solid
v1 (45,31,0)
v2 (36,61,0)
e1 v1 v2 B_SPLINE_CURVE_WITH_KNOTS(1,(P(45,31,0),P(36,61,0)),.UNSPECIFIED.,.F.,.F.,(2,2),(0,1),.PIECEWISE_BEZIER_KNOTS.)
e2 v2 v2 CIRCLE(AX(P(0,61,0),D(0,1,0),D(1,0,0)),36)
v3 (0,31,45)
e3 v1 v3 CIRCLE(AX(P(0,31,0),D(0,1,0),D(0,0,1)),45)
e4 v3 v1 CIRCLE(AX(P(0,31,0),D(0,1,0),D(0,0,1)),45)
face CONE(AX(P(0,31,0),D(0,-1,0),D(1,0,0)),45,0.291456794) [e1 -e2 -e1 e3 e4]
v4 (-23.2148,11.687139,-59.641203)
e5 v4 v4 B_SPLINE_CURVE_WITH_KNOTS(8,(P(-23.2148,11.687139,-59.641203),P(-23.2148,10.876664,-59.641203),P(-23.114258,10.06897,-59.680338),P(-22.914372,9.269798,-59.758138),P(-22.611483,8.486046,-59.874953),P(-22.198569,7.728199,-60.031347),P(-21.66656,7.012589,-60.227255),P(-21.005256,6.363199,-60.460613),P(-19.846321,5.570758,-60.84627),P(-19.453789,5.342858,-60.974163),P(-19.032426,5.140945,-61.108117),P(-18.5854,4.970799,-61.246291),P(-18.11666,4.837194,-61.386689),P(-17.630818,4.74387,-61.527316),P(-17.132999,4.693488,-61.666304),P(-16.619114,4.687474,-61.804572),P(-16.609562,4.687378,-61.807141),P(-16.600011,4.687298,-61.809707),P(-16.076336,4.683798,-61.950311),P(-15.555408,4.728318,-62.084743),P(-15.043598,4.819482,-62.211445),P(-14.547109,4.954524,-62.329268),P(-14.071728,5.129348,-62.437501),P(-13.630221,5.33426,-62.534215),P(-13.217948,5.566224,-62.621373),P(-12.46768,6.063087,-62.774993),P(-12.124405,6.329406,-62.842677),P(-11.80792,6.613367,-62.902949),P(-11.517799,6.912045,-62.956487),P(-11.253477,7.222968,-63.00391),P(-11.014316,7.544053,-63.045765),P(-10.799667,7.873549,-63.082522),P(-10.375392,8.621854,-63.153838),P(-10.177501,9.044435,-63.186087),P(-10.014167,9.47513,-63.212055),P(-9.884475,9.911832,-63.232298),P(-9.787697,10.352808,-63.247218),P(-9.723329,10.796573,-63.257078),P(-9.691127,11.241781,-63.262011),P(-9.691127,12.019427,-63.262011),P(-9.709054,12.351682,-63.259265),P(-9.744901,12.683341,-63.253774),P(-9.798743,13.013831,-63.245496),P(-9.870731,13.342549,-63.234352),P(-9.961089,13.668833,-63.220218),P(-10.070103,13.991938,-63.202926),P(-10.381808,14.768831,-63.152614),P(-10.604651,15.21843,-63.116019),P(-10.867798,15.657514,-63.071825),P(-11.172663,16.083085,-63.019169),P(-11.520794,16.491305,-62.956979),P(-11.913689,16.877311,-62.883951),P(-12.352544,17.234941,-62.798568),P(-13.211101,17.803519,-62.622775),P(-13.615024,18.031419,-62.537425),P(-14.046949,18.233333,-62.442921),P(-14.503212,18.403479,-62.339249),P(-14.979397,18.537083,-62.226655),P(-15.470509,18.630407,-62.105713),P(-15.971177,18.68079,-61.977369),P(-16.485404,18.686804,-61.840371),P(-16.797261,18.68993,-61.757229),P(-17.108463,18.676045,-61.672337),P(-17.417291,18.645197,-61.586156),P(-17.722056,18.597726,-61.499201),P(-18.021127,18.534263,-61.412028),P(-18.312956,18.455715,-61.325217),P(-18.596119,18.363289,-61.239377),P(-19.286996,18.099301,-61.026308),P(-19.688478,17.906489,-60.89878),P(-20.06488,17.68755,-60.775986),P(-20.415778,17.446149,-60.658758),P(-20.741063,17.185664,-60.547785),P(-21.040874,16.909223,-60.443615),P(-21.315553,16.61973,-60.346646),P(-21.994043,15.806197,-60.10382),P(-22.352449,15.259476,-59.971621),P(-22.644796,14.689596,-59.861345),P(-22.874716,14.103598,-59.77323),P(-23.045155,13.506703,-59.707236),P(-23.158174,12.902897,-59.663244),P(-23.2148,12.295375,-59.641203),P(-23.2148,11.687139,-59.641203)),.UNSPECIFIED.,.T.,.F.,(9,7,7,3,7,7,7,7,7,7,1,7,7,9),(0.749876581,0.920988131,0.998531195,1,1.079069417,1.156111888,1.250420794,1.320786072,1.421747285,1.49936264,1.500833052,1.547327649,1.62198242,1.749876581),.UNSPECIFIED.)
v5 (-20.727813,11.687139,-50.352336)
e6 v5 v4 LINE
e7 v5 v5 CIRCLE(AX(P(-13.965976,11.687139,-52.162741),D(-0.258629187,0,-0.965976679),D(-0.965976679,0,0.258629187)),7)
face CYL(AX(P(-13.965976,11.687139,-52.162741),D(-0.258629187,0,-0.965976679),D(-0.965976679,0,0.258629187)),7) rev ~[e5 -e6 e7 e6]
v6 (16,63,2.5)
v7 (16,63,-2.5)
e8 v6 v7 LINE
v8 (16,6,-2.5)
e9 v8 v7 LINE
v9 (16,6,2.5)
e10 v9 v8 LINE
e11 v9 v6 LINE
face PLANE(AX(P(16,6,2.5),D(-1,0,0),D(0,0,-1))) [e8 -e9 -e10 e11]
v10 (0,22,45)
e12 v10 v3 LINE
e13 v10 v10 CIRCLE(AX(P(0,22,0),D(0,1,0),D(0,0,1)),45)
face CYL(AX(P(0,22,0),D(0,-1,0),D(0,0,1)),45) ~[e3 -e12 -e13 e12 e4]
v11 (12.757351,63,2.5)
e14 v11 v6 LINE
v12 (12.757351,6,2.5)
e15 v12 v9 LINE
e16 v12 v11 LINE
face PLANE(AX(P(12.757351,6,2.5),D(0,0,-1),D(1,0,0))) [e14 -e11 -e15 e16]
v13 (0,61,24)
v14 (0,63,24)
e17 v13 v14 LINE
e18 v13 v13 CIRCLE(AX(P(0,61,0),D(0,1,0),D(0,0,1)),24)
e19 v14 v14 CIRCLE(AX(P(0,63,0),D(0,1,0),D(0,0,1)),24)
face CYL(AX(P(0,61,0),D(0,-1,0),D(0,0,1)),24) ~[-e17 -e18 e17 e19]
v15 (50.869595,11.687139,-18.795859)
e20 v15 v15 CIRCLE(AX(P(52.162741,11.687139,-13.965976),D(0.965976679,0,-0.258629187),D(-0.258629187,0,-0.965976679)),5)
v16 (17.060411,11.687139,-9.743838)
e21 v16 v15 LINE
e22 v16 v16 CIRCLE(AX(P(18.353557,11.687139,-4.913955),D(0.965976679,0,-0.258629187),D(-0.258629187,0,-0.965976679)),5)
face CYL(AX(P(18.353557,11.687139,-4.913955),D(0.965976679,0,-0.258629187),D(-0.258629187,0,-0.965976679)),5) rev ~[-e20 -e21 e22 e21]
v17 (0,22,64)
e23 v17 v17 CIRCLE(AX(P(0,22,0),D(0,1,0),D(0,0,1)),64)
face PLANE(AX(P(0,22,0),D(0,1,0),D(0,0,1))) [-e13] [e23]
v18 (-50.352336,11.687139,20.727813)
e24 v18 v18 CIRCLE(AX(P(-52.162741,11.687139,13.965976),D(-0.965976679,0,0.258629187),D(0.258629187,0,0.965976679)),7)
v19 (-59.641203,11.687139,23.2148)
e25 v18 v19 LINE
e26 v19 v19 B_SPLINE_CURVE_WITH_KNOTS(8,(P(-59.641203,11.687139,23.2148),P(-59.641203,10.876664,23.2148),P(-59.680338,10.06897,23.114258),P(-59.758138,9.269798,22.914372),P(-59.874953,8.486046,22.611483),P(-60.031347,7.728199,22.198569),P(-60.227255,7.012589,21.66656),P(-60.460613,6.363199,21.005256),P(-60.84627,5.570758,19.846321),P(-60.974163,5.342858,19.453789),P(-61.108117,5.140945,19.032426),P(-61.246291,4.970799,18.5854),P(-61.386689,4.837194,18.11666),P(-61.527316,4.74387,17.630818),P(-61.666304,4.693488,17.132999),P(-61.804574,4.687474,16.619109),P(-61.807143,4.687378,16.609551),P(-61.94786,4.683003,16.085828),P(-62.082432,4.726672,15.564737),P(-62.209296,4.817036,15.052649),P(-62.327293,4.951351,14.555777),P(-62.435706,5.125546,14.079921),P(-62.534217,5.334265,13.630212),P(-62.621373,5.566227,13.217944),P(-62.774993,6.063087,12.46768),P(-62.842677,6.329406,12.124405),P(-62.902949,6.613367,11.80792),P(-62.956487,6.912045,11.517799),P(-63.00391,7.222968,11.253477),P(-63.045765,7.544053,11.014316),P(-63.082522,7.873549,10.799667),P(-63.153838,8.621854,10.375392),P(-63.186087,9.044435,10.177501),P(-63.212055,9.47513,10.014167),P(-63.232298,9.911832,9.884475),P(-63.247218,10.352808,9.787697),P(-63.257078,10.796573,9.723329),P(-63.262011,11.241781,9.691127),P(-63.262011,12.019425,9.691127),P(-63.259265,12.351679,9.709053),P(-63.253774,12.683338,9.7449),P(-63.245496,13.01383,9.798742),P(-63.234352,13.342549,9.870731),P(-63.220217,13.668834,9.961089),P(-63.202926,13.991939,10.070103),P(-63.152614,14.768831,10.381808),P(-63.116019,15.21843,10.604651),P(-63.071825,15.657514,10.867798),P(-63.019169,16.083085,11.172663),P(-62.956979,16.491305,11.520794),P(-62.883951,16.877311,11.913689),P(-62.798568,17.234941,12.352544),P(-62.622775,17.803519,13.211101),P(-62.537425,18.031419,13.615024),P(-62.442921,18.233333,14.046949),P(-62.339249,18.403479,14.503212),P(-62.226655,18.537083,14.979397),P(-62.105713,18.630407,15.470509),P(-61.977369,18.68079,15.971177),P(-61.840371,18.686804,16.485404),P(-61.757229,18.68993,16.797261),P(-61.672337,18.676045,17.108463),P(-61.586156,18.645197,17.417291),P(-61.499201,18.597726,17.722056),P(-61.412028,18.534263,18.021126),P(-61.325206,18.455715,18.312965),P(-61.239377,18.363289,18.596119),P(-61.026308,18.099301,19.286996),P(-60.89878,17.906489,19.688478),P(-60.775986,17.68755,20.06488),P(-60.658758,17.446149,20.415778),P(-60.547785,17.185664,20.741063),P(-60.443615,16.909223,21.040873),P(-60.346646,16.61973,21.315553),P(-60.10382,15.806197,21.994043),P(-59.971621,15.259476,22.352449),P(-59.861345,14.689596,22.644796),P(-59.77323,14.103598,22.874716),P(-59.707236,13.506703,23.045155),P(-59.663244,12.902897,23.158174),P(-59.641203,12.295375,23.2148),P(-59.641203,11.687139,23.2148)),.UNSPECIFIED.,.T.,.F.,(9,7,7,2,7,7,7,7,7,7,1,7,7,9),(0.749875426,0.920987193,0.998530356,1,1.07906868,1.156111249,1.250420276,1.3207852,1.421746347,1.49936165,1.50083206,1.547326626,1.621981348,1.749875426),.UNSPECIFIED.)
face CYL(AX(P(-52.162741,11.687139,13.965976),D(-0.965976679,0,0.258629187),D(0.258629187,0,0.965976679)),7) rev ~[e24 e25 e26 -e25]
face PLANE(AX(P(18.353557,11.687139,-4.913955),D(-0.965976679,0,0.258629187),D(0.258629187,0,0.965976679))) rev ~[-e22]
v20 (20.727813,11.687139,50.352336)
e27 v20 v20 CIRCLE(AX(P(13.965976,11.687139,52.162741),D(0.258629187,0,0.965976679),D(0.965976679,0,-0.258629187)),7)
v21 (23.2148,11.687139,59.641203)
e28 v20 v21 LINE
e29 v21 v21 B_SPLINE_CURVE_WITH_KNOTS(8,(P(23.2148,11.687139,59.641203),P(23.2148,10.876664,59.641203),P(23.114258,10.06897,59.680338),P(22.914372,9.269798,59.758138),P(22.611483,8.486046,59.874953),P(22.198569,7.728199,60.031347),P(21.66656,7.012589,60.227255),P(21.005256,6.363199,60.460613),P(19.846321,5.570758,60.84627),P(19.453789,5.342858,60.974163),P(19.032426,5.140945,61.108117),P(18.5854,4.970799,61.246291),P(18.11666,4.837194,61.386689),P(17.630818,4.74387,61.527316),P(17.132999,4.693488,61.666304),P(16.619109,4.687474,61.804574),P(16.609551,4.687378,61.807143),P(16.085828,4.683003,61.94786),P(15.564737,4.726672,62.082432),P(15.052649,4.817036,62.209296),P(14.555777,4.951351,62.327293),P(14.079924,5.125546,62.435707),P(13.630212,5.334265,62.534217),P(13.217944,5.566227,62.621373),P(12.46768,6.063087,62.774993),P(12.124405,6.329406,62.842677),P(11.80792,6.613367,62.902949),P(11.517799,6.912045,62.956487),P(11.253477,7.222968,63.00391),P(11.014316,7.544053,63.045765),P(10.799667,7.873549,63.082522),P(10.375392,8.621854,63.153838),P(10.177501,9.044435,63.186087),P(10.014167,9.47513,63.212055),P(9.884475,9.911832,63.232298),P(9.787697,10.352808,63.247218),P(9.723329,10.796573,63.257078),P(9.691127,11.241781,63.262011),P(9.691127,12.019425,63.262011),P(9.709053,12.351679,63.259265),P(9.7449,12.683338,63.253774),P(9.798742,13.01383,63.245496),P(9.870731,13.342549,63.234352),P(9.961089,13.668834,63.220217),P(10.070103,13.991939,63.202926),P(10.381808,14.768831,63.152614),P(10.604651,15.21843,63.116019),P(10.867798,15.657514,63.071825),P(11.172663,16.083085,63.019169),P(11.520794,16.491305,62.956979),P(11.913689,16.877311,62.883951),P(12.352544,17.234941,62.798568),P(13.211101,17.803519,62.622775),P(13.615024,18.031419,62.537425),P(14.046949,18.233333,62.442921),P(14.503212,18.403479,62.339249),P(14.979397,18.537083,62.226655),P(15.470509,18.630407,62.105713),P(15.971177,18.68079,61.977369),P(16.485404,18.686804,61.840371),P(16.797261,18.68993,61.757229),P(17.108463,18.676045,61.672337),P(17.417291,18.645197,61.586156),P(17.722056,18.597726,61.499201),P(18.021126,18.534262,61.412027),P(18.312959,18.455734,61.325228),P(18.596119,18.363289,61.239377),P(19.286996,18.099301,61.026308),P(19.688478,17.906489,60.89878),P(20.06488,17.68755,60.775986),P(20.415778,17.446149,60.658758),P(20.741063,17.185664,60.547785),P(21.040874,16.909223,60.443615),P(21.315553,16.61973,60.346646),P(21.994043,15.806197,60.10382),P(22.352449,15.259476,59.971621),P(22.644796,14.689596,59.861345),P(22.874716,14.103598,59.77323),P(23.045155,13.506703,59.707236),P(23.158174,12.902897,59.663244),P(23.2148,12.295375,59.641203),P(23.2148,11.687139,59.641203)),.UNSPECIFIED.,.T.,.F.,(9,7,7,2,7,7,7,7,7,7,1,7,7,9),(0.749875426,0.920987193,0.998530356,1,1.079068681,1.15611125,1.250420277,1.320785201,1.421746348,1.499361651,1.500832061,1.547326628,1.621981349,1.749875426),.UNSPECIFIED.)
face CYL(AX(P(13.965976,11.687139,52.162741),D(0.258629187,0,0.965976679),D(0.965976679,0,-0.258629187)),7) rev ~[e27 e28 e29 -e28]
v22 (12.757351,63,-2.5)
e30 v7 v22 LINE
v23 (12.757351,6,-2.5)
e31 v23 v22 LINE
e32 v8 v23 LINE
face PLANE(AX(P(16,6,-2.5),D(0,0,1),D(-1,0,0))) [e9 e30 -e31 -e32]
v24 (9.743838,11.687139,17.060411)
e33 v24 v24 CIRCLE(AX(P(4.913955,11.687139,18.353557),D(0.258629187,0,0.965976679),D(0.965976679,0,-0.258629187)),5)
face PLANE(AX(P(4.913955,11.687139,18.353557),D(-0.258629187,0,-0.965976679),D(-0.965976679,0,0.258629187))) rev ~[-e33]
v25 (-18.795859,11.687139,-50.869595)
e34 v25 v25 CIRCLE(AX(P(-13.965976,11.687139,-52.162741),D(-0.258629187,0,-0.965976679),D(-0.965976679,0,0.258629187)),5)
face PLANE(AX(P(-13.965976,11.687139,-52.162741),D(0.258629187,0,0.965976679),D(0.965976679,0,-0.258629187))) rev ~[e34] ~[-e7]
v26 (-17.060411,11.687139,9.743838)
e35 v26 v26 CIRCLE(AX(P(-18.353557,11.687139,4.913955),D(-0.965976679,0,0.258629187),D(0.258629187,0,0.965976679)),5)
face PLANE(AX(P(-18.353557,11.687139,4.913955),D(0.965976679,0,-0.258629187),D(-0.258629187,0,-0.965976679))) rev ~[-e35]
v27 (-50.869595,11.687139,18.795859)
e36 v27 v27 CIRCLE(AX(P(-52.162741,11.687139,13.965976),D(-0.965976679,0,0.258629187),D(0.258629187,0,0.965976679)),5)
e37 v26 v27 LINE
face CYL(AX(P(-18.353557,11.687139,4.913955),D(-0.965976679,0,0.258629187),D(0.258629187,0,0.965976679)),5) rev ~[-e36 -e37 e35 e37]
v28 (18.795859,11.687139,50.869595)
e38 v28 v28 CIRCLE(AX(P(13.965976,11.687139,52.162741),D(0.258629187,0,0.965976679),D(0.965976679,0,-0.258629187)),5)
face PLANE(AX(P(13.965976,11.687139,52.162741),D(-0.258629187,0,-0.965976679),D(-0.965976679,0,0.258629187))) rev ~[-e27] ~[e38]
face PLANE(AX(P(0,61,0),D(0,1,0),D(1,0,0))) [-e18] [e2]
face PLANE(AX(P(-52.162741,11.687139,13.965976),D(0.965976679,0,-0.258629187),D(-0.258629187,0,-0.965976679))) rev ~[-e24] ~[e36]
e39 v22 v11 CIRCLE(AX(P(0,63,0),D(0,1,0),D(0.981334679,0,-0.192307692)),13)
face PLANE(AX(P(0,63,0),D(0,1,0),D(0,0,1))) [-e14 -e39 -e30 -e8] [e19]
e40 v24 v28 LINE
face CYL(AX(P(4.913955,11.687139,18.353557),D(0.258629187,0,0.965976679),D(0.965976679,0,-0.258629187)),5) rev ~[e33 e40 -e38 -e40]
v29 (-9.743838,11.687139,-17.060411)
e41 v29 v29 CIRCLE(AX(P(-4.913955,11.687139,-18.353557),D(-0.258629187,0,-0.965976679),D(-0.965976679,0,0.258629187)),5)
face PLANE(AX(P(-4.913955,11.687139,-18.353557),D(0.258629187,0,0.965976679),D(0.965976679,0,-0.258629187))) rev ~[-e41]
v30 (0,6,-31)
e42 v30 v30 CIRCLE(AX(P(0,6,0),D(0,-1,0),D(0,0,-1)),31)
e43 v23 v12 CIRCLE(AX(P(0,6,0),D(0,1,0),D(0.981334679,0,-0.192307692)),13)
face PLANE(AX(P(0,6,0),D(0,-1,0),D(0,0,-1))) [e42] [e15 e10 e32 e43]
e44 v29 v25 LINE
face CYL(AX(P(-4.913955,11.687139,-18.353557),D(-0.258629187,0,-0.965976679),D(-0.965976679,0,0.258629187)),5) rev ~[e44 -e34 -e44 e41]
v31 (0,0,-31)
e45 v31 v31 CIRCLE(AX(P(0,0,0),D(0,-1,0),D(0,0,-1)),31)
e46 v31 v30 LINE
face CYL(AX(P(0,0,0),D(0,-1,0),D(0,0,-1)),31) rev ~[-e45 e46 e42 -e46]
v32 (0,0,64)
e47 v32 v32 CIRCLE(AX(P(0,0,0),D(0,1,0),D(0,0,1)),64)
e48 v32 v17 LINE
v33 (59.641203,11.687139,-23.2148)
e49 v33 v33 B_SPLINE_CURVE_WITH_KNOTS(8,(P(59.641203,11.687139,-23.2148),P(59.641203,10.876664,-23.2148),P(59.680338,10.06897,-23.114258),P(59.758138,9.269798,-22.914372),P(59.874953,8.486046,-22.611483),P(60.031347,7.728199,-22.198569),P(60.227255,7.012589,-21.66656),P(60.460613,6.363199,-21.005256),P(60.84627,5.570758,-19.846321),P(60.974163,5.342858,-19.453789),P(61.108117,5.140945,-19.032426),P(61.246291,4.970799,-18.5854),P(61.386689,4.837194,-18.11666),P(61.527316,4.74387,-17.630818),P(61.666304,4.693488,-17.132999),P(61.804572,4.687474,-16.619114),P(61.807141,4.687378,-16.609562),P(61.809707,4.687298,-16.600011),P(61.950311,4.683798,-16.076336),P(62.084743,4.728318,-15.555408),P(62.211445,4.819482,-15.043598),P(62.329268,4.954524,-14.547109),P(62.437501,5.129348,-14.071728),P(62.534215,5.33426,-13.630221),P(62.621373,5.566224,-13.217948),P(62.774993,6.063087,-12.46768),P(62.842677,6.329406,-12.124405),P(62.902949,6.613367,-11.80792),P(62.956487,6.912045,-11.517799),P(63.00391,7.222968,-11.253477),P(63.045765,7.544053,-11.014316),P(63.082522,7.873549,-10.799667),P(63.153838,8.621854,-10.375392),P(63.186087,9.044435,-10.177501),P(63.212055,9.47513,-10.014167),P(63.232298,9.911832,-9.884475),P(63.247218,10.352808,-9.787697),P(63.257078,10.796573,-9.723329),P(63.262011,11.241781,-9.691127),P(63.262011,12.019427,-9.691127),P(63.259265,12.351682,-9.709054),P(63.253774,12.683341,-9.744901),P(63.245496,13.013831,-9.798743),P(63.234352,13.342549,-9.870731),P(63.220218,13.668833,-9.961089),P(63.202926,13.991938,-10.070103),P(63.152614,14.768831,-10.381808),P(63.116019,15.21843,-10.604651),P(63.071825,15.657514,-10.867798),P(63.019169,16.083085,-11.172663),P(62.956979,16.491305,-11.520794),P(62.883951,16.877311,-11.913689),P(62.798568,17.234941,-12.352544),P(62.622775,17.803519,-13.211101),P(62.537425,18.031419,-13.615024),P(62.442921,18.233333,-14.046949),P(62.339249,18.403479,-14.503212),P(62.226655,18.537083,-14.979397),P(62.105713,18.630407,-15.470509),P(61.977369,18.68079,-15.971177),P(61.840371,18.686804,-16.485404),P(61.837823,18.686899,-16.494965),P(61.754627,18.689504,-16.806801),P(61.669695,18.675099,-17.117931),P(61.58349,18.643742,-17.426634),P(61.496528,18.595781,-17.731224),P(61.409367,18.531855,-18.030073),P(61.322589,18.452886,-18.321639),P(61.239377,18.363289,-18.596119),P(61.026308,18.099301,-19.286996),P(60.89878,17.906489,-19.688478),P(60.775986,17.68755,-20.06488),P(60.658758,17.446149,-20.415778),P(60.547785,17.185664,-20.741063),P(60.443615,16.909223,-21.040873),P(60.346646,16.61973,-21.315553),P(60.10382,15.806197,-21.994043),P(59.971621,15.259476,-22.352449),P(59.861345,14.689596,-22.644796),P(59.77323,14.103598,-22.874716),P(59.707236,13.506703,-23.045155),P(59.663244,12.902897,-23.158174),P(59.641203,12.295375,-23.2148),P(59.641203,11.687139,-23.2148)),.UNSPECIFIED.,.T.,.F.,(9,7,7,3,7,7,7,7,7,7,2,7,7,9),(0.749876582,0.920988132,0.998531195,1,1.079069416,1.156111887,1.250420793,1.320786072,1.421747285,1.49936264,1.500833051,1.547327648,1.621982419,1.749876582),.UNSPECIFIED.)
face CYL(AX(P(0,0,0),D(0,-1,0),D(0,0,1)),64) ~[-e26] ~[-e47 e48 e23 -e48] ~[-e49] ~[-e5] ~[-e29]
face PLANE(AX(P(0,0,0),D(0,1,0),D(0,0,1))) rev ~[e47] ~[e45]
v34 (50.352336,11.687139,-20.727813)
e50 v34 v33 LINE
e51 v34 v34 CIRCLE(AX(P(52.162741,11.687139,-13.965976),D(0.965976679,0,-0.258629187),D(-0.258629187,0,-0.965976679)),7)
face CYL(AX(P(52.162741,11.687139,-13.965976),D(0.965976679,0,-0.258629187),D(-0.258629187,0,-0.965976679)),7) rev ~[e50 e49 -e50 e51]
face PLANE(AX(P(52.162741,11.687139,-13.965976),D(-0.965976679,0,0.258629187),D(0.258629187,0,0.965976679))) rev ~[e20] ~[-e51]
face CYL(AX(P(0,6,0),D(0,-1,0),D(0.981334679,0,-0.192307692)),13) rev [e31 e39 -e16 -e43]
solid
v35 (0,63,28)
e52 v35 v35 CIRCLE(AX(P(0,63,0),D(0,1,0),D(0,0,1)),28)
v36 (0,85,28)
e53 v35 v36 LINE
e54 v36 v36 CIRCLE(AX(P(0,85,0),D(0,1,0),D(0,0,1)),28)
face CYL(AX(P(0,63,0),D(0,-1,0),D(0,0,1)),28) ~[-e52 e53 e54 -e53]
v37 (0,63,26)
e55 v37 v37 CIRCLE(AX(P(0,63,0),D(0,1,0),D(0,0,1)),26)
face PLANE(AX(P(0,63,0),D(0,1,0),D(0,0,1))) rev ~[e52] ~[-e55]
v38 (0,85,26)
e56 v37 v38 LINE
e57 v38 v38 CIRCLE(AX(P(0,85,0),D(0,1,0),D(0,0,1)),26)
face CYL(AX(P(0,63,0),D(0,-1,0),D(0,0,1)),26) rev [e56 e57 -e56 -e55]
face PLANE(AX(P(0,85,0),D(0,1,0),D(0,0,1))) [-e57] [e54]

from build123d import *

# Parameters (mm, degrees)
BASE_FLANGE_SKETCH_R          = 64
BASE_FLANGE_128_DEPTH         = 22
COLLAR_SKETCH_R               = 45
COLLAR_90_DEPTH               = 9
LOFT_BASE_PROFILE_R           = 45
LOFT_TOP_PROFILE_72_R         = 36
TOP_STEP_SKETCH_R             = 24
TOP_STEP_48_DEPTH             = 2
TUBE_SKETCH_R                 = 28
TUBE_SKETCH_R_2               = 26
TUBE_56X_52_DEPTH             = 22
RADIAL_HOLES_PATTERN_4X_COUNT = 4
BOTTOM_RECESS_SKETCH_R        = 31
BOTTOM_RECESS_62_DEPTH        = 6
BOTTOM_SLOT_CUT_DEPTH         = 57


with BuildPart() as part:
    # Base Flange Sketch → Base Flange Ø128 (new body)
    with BuildSketch(Plane(origin=(0, 0, 0), x_dir=(1, 0, 0), z_dir=(0, 1, 0))):
        with Locations(Location((0, 0, 0), (0, 0, 270))):
            Circle(BASE_FLANGE_SKETCH_R)
    extrude(amount=BASE_FLANGE_128_DEPTH)

    # Collar Sketch → Collar Ø90 (add)
    with BuildSketch(Plane(origin=(0, 22, 0), x_dir=(1, 0, 0), z_dir=(0, 1, 0))):
        with Locations(Location((0, 0, 0), (0, 0, 270))):
            Circle(COLLAR_SKETCH_R)
    extrude(amount=COLLAR_90_DEPTH)

    # Loft Base Profile → Conical Transition Loft section 0
    with BuildSketch(Plane(origin=(0, 31, 0), x_dir=(1, 0, 0), z_dir=(0, 1, 0))):
        Circle(LOFT_BASE_PROFILE_R)
    # Loft Top Profile Ø72 → Conical Transition Loft section 1
    with BuildSketch(Plane(origin=(0, 61, 0), x_dir=(1, 0, 0), z_dir=(0, 1, 0))):
        Circle(LOFT_TOP_PROFILE_72_R)
    loft()

    # Top Step Sketch → Top Step Ø48 (add)
    with BuildSketch(Plane(origin=(0, 61, 0), x_dir=(1, 0, 0), z_dir=(0, 1, 0))):
        with Locations(Location((0, 0, 0), (0, 0, 270))):
            Circle(TOP_STEP_SKETCH_R)
    extrude(amount=TOP_STEP_48_DEPTH)

    # Sketch15 → Radial C-Bore Hole Ø10 (revolve, cut)
    with BuildSketch(Plane(origin=(61.822507432, 11.6871388, -16.552267966), x_dir=(-0.2586291869671418, 0, -0.9659766786256878), z_dir=(0, 1, 0))):
        Polygon((0, 0), (0, 45), (5, 45), (5, 10), (7, 10), (7, 0), align=None)
    radial_c_bore_hole_10 = revolve(axis=Axis((-44.434927217, 11.6871388, 11.8969426), (0.9659766786256878, 0, -0.25862918696714177)), mode=Mode.SUBTRACT)

    # Radial Holes Pattern 4x: Radial C-Bore Hole Ø10 ×4 about axis
    radial_holes_pattern_4x_axis = Axis((0, 0, 0), (0, 1, 0))
    for i in range(1, RADIAL_HOLES_PATTERN_4X_COUNT):
        add(radial_c_bore_hole_10.rotate(radial_holes_pattern_4x_axis, i * 360 / RADIAL_HOLES_PATTERN_4X_COUNT), mode=Mode.SUBTRACT)

    # Bottom Recess Sketch → Bottom Recess Ø62 (cut)
    with BuildSketch(Plane.XZ):
        with Locations(Location((0, 0, 0), (0, 0, 270))):
            Circle(BOTTOM_RECESS_SKETCH_R)
    extrude(amount=-BOTTOM_RECESS_62_DEPTH, mode=Mode.SUBTRACT)

    # Bottom Slot Sketch → Bottom Slot Cut (cut)
    with BuildSketch(Plane.XZ.offset(-6)):
        with BuildLine():
            Line((12.757350822, 2.5), (16, 2.5))
            Line((16, 2.5), (16, -2.5))
            Line((16, -2.5), (12.757350822, -2.5))
            ThreePointArc((12.757350822, -2.5), (-13, 0), (12.757350822, 2.5))
        make_face()
    extrude(amount=-BOTTOM_SLOT_CUT_DEPTH, mode=Mode.SUBTRACT)


with BuildPart() as body_2:
    # Tube Sketch → Tube Ø56xØ52 (new body)
    with BuildSketch(Plane(origin=(0, 63, 0), x_dir=(1, 0, 0), z_dir=(0, 1, 0))):
        with Locations(Location((0, 0, 0), (0, 0, 270))):
            Circle(TUBE_SKETCH_R)
        with Locations(Location((0, 0, 0), (0, 0, 270))):
            Circle(TUBE_SKETCH_R_2, mode=Mode.SUBTRACT)
    extrude(amount=TUBE_56X_52_DEPTH)


solid = Compound([part.part, body_2.part])
